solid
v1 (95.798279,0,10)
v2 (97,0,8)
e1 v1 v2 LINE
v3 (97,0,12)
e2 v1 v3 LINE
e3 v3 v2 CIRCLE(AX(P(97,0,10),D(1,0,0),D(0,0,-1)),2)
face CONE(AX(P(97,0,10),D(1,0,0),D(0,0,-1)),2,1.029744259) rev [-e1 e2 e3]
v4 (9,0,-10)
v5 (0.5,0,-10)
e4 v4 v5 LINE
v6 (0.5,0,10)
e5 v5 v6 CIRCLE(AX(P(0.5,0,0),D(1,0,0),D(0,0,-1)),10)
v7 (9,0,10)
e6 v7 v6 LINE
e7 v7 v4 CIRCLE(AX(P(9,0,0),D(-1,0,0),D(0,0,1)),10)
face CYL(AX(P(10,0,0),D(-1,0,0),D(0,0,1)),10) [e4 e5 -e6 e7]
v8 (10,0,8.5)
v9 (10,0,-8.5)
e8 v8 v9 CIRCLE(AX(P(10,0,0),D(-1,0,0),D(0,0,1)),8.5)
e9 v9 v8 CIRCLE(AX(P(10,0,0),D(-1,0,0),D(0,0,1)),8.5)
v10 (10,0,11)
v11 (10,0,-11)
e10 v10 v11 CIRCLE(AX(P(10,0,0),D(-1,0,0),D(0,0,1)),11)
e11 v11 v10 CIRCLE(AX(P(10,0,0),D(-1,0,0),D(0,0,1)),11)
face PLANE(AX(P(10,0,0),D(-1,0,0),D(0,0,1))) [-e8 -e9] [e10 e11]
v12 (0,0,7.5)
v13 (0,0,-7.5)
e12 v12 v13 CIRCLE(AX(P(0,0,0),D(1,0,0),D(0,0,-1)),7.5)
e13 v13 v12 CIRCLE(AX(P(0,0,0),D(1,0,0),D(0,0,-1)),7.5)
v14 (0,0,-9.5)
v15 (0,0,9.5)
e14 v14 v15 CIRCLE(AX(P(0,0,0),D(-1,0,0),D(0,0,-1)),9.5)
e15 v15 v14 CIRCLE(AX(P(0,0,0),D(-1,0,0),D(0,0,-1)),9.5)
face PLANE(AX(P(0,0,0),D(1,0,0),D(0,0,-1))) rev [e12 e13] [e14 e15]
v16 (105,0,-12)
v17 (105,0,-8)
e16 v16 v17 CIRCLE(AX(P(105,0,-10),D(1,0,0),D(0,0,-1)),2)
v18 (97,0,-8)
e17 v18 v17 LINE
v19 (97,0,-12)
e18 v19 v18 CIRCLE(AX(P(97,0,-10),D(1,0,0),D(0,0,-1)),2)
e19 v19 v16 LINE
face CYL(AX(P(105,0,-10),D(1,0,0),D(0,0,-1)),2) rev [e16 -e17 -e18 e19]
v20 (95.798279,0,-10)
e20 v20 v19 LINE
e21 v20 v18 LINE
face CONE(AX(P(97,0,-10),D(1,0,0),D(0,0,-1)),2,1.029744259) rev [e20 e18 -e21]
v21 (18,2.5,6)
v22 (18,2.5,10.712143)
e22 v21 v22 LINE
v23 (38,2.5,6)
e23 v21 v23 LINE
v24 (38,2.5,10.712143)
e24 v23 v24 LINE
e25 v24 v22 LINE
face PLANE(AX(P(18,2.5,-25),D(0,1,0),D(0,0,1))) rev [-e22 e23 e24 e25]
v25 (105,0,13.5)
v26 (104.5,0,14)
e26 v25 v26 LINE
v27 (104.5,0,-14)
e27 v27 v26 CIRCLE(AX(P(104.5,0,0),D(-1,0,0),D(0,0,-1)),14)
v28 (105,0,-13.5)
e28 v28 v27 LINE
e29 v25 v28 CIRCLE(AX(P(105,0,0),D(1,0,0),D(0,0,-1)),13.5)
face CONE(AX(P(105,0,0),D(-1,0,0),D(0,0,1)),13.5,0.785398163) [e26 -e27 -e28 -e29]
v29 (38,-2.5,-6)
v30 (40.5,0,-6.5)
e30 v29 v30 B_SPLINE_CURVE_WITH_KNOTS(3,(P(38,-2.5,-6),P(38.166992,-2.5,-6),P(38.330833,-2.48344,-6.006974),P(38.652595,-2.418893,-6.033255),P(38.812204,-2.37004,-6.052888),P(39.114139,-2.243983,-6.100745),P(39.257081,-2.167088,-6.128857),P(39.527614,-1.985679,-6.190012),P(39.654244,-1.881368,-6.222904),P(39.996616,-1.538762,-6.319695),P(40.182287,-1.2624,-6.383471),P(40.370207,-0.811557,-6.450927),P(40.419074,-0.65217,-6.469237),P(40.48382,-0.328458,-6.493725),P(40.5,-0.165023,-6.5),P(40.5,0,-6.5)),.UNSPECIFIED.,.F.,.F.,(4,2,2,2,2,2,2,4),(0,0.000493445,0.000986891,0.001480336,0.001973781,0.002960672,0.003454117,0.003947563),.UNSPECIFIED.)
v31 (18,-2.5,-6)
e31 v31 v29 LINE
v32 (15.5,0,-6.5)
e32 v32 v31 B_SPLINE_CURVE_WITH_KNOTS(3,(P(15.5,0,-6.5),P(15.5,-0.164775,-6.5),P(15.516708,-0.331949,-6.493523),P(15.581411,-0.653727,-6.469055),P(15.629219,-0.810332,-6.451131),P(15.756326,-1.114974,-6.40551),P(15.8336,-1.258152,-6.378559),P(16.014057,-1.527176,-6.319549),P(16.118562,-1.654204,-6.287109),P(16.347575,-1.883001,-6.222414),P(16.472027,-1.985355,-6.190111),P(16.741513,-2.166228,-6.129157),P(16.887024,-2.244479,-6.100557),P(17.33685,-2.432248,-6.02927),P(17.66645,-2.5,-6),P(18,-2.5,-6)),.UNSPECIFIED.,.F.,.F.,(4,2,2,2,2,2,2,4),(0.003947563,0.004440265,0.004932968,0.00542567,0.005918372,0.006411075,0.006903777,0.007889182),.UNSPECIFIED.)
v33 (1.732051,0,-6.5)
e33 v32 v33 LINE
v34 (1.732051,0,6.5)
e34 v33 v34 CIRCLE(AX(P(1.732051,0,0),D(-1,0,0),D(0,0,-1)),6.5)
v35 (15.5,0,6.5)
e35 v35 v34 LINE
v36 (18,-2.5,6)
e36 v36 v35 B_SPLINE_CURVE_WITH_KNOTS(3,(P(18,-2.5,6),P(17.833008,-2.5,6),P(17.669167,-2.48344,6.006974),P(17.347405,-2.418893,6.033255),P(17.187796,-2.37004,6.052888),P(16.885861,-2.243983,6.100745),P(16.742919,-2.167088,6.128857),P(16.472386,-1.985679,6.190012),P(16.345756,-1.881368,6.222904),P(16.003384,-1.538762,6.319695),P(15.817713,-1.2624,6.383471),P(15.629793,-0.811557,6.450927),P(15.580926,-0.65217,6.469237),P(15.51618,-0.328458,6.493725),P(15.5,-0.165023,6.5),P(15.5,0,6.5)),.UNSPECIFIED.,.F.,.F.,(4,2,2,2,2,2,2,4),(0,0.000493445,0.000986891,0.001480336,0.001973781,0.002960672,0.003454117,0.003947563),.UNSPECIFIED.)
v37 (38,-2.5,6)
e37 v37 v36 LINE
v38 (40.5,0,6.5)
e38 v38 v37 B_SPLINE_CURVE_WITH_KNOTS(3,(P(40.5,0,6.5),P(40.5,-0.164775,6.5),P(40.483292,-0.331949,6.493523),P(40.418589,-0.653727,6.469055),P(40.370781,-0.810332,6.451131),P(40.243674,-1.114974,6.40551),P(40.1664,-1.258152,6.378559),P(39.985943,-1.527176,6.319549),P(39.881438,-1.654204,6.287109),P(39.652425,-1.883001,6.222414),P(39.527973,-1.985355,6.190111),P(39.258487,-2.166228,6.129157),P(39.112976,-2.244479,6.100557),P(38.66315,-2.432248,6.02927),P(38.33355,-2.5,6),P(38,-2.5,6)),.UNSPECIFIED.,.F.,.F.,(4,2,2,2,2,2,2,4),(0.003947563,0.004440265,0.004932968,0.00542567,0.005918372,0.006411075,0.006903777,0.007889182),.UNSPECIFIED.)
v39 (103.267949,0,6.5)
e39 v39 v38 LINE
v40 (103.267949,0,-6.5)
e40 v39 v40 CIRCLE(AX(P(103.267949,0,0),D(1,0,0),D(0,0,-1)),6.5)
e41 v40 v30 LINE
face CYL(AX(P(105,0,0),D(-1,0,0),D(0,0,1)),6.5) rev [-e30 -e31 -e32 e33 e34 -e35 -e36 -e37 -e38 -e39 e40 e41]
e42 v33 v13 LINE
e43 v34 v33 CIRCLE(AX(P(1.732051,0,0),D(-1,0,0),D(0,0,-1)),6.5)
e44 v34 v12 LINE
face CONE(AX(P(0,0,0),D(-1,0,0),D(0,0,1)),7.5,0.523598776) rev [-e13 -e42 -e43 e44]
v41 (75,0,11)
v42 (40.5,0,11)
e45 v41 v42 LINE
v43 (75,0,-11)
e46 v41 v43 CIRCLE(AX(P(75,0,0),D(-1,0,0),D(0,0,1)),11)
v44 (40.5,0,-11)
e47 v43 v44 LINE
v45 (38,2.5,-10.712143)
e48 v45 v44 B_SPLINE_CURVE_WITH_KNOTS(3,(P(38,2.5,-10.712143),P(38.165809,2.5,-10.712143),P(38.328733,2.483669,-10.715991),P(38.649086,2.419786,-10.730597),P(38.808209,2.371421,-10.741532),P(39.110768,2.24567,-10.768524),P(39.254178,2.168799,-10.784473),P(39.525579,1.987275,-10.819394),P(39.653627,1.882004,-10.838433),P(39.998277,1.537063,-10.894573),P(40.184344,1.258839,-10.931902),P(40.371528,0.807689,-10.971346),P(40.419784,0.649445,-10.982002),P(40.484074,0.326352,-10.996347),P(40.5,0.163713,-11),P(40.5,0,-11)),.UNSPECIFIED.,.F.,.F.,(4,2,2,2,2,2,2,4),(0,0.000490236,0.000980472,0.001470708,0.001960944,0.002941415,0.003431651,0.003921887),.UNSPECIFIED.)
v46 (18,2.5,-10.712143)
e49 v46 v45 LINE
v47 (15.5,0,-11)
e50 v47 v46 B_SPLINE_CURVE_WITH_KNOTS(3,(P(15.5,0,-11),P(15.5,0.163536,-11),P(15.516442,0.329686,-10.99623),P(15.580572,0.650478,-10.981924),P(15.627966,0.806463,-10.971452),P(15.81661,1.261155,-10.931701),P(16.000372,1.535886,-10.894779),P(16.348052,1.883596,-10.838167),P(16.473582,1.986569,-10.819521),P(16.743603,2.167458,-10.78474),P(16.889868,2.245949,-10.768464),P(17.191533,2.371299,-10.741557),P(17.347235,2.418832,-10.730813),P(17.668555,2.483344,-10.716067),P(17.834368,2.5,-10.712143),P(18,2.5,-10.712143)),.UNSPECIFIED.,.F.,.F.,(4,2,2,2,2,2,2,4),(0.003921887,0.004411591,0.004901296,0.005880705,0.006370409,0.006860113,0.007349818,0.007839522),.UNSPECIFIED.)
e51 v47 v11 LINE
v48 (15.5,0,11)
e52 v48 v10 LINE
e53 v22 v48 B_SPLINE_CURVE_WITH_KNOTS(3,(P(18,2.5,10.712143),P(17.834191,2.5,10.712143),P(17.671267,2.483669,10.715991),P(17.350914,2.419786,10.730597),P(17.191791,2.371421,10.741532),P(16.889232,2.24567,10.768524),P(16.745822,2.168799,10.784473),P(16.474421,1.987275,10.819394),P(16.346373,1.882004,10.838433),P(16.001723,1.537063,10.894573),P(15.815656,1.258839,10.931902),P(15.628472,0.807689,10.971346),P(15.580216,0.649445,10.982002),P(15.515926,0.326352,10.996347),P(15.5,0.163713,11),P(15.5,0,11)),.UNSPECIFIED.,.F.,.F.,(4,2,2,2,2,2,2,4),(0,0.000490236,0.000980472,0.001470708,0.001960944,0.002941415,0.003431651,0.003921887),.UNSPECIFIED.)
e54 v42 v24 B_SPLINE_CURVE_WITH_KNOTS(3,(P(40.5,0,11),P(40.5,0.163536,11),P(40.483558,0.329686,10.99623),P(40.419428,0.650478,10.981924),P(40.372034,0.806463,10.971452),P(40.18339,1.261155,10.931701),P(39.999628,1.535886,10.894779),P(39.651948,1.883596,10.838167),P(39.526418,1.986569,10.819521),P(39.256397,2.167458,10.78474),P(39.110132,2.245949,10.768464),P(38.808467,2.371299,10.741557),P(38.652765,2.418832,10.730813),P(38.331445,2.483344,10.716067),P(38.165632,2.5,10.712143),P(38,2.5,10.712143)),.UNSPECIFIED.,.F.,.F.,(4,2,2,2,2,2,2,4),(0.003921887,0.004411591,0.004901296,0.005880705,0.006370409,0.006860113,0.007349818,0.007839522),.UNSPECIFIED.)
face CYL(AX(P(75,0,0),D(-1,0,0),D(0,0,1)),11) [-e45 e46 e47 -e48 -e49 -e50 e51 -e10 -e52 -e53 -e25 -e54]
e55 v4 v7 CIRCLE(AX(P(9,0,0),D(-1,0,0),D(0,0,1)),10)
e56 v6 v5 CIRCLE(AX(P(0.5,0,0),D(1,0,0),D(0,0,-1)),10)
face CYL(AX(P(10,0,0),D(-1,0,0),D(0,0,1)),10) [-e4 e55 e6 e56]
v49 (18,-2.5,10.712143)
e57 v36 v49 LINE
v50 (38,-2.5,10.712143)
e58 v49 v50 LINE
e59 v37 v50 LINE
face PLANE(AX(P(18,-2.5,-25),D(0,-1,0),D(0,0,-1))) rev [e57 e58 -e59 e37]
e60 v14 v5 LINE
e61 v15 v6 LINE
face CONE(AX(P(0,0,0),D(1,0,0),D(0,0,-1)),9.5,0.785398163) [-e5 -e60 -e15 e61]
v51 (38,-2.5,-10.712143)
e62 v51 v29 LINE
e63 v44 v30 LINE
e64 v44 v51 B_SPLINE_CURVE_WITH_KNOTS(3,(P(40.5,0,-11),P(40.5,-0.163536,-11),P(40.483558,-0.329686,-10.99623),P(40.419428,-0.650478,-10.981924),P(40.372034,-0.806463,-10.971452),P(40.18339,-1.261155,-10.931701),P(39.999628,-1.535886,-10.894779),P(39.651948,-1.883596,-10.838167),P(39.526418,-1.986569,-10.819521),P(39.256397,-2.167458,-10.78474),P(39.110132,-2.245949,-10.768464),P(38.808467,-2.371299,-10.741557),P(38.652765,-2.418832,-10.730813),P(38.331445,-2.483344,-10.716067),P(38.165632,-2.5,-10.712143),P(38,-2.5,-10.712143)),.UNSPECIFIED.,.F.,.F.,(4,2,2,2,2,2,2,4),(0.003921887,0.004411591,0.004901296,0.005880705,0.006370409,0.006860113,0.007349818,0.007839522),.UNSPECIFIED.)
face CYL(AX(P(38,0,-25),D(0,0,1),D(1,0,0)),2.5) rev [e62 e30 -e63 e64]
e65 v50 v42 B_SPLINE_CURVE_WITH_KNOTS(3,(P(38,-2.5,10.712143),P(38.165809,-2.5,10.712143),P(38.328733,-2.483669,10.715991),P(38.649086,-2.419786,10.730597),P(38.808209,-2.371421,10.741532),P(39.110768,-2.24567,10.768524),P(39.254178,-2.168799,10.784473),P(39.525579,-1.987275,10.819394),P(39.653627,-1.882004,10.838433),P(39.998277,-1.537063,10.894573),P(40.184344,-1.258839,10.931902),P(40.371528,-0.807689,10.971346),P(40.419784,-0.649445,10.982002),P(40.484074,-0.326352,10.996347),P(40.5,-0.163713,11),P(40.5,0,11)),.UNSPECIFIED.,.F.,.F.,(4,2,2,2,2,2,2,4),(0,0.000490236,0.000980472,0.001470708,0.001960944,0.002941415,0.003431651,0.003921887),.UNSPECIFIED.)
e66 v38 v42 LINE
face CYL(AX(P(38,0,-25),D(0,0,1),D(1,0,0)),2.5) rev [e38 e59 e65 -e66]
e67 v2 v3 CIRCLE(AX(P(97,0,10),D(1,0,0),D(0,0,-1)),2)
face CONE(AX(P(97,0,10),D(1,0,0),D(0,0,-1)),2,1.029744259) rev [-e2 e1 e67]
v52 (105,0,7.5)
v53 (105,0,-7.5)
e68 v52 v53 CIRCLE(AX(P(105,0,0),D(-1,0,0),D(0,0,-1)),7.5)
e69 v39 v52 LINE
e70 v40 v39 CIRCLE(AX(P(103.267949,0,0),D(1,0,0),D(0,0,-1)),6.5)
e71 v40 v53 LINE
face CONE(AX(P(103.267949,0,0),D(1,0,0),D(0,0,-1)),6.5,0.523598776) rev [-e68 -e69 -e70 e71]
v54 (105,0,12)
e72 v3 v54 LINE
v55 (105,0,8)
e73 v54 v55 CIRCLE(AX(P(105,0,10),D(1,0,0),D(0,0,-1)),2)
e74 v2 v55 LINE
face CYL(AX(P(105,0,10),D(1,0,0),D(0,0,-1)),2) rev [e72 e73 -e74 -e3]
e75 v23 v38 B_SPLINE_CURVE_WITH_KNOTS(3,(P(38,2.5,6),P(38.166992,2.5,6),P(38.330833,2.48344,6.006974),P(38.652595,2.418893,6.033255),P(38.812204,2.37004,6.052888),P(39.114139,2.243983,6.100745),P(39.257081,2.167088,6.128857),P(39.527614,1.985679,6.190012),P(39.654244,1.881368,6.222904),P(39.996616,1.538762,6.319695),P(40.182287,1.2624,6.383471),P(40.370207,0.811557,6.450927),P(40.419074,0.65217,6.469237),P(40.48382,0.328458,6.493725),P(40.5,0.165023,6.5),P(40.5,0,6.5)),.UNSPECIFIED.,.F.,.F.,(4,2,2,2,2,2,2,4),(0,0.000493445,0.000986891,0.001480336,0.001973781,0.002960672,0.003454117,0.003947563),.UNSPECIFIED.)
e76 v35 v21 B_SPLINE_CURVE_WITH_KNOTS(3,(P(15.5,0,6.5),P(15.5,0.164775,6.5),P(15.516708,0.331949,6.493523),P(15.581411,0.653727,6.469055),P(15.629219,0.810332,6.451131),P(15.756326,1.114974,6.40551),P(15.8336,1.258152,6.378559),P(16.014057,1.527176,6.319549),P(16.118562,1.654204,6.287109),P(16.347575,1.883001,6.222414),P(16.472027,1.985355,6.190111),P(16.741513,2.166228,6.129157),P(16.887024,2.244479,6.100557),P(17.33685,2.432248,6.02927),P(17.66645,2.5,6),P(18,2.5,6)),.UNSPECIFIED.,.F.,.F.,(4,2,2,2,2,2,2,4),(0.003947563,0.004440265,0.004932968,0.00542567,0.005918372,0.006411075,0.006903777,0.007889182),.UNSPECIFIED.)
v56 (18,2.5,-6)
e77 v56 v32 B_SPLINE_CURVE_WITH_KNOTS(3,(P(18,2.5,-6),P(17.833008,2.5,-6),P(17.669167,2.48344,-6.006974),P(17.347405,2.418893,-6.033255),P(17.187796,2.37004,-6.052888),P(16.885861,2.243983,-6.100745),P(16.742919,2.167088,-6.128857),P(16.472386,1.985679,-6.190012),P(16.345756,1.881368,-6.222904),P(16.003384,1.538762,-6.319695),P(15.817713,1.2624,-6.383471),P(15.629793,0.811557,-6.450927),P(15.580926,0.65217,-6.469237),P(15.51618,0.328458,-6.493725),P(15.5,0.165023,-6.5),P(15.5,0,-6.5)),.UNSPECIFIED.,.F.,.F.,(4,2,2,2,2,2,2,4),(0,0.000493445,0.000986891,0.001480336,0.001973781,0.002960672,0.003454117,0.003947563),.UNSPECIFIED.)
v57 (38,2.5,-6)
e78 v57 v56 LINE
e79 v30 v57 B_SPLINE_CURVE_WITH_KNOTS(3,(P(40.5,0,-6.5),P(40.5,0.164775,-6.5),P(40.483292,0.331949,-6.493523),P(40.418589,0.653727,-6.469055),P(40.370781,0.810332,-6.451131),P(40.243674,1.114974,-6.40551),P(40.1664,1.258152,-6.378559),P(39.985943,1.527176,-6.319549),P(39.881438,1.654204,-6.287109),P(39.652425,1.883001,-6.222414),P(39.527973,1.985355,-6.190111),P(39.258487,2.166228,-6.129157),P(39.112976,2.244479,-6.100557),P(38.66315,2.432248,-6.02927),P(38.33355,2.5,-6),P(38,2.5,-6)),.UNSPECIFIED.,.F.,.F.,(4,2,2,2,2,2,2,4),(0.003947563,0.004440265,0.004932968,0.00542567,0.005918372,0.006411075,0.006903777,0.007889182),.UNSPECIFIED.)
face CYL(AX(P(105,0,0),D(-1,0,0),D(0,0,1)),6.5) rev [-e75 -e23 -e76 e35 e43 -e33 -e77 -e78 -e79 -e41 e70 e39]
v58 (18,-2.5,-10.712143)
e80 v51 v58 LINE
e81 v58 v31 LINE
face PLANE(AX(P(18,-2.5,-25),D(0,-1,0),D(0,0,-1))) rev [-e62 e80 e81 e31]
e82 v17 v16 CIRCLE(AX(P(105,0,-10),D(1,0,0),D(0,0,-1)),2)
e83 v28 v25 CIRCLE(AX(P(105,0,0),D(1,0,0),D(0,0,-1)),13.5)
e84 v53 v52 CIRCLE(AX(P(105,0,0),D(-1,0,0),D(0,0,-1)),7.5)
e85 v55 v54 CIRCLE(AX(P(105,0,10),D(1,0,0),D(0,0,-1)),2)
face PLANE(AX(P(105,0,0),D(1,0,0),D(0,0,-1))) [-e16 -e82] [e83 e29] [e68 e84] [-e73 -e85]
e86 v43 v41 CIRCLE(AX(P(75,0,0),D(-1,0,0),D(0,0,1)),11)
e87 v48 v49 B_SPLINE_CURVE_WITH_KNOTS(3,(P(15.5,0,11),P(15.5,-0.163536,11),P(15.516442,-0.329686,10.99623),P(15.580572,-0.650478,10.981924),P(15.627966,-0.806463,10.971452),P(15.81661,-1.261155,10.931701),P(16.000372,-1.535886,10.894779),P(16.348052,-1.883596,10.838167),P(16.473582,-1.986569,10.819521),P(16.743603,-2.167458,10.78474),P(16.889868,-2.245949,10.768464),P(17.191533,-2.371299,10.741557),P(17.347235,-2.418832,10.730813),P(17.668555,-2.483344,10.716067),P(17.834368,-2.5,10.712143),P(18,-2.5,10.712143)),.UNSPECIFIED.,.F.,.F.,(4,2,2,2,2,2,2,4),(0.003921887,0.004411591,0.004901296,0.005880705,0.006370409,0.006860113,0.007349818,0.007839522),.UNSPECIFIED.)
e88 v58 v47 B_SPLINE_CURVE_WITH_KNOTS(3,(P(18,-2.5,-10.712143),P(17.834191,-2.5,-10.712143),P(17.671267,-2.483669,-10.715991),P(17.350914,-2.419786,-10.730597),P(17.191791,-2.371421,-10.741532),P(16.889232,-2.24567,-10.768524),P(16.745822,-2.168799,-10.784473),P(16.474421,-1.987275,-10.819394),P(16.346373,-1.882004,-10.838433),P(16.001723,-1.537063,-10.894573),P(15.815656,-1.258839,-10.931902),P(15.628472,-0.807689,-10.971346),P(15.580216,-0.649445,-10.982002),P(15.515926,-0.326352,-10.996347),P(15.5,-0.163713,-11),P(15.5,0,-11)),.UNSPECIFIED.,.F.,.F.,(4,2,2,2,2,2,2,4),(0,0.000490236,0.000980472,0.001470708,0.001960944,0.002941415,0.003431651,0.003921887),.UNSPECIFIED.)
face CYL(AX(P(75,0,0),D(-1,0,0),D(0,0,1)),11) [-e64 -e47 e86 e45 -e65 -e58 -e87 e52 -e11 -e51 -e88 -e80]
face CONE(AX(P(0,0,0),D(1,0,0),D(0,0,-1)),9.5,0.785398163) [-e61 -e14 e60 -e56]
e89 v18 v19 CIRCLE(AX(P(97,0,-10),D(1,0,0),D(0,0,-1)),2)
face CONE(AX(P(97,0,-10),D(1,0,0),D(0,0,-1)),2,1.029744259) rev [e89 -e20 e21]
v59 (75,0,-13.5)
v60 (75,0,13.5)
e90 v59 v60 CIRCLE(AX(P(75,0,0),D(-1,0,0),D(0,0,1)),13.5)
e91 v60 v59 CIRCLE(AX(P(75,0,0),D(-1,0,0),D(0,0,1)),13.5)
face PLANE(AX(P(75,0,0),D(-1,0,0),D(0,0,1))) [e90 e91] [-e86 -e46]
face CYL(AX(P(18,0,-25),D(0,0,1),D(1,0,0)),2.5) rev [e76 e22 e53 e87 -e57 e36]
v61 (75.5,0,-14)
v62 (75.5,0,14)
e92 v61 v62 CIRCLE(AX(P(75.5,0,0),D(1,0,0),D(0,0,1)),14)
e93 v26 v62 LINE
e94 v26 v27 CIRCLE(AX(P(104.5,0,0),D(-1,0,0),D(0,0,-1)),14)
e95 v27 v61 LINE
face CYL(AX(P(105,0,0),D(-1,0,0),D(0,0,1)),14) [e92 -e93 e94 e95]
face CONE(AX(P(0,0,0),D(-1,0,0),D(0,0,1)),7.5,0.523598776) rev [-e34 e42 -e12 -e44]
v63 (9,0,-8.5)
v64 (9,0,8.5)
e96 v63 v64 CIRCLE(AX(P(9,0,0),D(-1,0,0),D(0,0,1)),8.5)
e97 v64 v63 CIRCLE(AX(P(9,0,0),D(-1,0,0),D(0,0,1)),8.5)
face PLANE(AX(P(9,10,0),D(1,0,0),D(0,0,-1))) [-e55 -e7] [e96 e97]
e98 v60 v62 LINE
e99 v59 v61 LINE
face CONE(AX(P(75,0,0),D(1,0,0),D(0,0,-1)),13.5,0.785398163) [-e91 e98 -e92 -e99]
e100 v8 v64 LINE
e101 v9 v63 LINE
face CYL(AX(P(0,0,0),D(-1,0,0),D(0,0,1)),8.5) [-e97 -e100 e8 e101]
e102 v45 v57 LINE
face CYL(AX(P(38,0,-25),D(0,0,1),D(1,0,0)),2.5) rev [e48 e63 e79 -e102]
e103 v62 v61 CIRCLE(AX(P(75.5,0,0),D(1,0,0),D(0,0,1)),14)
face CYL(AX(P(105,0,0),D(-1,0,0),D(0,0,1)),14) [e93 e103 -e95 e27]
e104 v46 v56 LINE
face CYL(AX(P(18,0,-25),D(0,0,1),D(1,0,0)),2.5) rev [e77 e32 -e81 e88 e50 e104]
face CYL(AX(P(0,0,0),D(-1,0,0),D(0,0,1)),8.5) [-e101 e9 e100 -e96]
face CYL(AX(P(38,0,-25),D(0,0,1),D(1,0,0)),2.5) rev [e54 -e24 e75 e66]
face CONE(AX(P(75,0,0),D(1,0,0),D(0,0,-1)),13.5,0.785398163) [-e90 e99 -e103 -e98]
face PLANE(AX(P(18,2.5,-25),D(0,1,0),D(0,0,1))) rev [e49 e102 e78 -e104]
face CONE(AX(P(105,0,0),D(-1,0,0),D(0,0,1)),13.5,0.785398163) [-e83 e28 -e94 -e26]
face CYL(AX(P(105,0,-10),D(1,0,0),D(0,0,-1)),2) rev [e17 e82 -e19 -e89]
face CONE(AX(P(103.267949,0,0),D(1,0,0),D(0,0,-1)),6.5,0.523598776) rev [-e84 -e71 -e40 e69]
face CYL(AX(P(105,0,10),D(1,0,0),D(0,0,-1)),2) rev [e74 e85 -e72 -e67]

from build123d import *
from OCP.BRepFilletAPI import BRepFilletAPI_MakeChamfer

# Parameters (mm, degrees)
SKETCH_1_R                = 14
SKETCH_1_R_2              = 6.5
EXTRUDE_1_DEPTH           = 105
SKETCH_2_R                = 14
SKETCH_2_R_2              = 11
CUT_EXTRUDE_1_DEPTH       = 75
CUT_EXTRUDE_2_DEPTH       = 25
SKETCH_7_R                = 11
SKETCH_7_R_2              = 10
CUT_EXTRUDE_3_DEPTH       = 10
SKETCH_8_W                = 1
SKETCH_8_H                = 1.5
CHAMFER_1_SIZE            = 0.5
HOLE_WIZARD_4_0_4_1_D     = 4
HOLE_WIZARD_4_0_4_1_DEPTH = 8
HOLE_WIZARD_4_0_4_1_TIP   = 1.201721238
CHAMFER_2_SIZE            = 1
CHAMFER_2_SIZE2           = 1.732050808


with BuildPart() as part:
    # 草图1 → 凸台-拉伸1 (new body)
    with BuildSketch(Plane(origin=(0, 0, 0), x_dir=(0, 0, -1), z_dir=(1, 0, 0))):
        Circle(SKETCH_1_R)
        Circle(SKETCH_1_R_2, mode=Mode.SUBTRACT)
    extrude(amount=EXTRUDE_1_DEPTH)

    # 草图2 → 切除-拉伸1 (cut)
    with BuildSketch(Plane.ZY):
        Circle(SKETCH_2_R)
        Circle(SKETCH_2_R_2, mode=Mode.SUBTRACT)
    extrude(amount=-CUT_EXTRUDE_1_DEPTH, mode=Mode.SUBTRACT)

    # 草图4 → 切除-拉伸2 (cut, symmetric)
    with BuildSketch(Plane.XY):
        with BuildLine():
            Line((18, 2.5), (38, 2.5))
            ThreePointArc((38, 2.5), (40.5, 0), (38, -2.5))
            Line((38, -2.5), (18, -2.5))
            ThreePointArc((18, -2.5), (15.5, 0), (18, 2.5))
        make_face()
    extrude(amount=CUT_EXTRUDE_2_DEPTH, both=True, mode=Mode.SUBTRACT)

    # 草图7 → 切除-拉伸3 (cut)
    with BuildSketch(Plane.ZY):
        Circle(SKETCH_7_R)
        Circle(SKETCH_7_R_2, mode=Mode.SUBTRACT)
    extrude(amount=-CUT_EXTRUDE_3_DEPTH, mode=Mode.SUBTRACT)

    # 草图8 → 切除-旋转2 (revolve, cut)
    with BuildSketch(Plane.XY, mode=Mode.PRIVATE) as cut_revolve_2_sk:
        with Locations((9.5, 9.25)):
            Rectangle(SKETCH_8_W, SKETCH_8_H)
    revolve(cut_revolve_2_sk.sketch.rotate(Axis((0, 0, 0), (1, 0, 0)), 90), axis=Axis((0, 0, 0), (1, 0, 0)), mode=Mode.SUBTRACT)

    # 倒角1
    chamfer_1_edges = [part.edges().sort_by_distance(p)[0] for p in [
        (75, 0, 14),
        (105, 0, 14),
        (0, 0, -10),
    ]]
    chamfer(chamfer_1_edges, length=CHAMFER_1_SIZE)

    # Ø4.0 (4) 直径孔1
    with Locations(Plane(origin=(105, 0, 0), x_dir=(0, 0, -1), z_dir=(1, 0, 0))):
        with Locations((-10, 0), (10, 0)):
            Hole(HOLE_WIZARD_4_0_4_1_D / 2, depth=HOLE_WIZARD_4_0_4_1_DEPTH)
            with Locations((0, 0, -(HOLE_WIZARD_4_0_4_1_DEPTH + HOLE_WIZARD_4_0_4_1_TIP / 2))):  # 118° drill point
                Cone(0, HOLE_WIZARD_4_0_4_1_D / 2, HOLE_WIZARD_4_0_4_1_TIP, mode=Mode.SUBTRACT)

    # 倒角2: one chamfer whose edges measure the first distance from different faces: ONE call of the kernel's chamfer builder (chamfer() names one face for all edges)
    chamfer_2_edges_1 = [part.edges().sort_by_distance(p)[0] for p in [
        (0, 0, 6.5),
    ]]
    chamfer_2_side_1 = [part.faces().sort_by_distance(p)[0] for p in [
        (0, 0, -9.231299423),
    ]]
    chamfer_2_edges_2 = [part.edges().sort_by_distance(p)[0] for p in [
        (105, 0, 6.5),
    ]]
    chamfer_2_side_2 = [part.faces().sort_by_distance(p)[0] for p in [
        (105, 0, 13.118162338),
    ]]
    chamfer_2 = BRepFilletAPI_MakeChamfer(part.part.solid().wrapped)
    for e in chamfer_2_edges_1:
        chamfer_2.Add(CHAMFER_2_SIZE, CHAMFER_2_SIZE2, e.wrapped, chamfer_2_side_1[0].wrapped)  # the first distance lies on this face
    for e in chamfer_2_edges_2:
        chamfer_2.Add(CHAMFER_2_SIZE, CHAMFER_2_SIZE2, e.wrapped, chamfer_2_side_2[0].wrapped)  # the first distance lies on this face
    add(Compound.cast(chamfer_2.Shape()), mode=Mode.REPLACE)


solid = part.part
